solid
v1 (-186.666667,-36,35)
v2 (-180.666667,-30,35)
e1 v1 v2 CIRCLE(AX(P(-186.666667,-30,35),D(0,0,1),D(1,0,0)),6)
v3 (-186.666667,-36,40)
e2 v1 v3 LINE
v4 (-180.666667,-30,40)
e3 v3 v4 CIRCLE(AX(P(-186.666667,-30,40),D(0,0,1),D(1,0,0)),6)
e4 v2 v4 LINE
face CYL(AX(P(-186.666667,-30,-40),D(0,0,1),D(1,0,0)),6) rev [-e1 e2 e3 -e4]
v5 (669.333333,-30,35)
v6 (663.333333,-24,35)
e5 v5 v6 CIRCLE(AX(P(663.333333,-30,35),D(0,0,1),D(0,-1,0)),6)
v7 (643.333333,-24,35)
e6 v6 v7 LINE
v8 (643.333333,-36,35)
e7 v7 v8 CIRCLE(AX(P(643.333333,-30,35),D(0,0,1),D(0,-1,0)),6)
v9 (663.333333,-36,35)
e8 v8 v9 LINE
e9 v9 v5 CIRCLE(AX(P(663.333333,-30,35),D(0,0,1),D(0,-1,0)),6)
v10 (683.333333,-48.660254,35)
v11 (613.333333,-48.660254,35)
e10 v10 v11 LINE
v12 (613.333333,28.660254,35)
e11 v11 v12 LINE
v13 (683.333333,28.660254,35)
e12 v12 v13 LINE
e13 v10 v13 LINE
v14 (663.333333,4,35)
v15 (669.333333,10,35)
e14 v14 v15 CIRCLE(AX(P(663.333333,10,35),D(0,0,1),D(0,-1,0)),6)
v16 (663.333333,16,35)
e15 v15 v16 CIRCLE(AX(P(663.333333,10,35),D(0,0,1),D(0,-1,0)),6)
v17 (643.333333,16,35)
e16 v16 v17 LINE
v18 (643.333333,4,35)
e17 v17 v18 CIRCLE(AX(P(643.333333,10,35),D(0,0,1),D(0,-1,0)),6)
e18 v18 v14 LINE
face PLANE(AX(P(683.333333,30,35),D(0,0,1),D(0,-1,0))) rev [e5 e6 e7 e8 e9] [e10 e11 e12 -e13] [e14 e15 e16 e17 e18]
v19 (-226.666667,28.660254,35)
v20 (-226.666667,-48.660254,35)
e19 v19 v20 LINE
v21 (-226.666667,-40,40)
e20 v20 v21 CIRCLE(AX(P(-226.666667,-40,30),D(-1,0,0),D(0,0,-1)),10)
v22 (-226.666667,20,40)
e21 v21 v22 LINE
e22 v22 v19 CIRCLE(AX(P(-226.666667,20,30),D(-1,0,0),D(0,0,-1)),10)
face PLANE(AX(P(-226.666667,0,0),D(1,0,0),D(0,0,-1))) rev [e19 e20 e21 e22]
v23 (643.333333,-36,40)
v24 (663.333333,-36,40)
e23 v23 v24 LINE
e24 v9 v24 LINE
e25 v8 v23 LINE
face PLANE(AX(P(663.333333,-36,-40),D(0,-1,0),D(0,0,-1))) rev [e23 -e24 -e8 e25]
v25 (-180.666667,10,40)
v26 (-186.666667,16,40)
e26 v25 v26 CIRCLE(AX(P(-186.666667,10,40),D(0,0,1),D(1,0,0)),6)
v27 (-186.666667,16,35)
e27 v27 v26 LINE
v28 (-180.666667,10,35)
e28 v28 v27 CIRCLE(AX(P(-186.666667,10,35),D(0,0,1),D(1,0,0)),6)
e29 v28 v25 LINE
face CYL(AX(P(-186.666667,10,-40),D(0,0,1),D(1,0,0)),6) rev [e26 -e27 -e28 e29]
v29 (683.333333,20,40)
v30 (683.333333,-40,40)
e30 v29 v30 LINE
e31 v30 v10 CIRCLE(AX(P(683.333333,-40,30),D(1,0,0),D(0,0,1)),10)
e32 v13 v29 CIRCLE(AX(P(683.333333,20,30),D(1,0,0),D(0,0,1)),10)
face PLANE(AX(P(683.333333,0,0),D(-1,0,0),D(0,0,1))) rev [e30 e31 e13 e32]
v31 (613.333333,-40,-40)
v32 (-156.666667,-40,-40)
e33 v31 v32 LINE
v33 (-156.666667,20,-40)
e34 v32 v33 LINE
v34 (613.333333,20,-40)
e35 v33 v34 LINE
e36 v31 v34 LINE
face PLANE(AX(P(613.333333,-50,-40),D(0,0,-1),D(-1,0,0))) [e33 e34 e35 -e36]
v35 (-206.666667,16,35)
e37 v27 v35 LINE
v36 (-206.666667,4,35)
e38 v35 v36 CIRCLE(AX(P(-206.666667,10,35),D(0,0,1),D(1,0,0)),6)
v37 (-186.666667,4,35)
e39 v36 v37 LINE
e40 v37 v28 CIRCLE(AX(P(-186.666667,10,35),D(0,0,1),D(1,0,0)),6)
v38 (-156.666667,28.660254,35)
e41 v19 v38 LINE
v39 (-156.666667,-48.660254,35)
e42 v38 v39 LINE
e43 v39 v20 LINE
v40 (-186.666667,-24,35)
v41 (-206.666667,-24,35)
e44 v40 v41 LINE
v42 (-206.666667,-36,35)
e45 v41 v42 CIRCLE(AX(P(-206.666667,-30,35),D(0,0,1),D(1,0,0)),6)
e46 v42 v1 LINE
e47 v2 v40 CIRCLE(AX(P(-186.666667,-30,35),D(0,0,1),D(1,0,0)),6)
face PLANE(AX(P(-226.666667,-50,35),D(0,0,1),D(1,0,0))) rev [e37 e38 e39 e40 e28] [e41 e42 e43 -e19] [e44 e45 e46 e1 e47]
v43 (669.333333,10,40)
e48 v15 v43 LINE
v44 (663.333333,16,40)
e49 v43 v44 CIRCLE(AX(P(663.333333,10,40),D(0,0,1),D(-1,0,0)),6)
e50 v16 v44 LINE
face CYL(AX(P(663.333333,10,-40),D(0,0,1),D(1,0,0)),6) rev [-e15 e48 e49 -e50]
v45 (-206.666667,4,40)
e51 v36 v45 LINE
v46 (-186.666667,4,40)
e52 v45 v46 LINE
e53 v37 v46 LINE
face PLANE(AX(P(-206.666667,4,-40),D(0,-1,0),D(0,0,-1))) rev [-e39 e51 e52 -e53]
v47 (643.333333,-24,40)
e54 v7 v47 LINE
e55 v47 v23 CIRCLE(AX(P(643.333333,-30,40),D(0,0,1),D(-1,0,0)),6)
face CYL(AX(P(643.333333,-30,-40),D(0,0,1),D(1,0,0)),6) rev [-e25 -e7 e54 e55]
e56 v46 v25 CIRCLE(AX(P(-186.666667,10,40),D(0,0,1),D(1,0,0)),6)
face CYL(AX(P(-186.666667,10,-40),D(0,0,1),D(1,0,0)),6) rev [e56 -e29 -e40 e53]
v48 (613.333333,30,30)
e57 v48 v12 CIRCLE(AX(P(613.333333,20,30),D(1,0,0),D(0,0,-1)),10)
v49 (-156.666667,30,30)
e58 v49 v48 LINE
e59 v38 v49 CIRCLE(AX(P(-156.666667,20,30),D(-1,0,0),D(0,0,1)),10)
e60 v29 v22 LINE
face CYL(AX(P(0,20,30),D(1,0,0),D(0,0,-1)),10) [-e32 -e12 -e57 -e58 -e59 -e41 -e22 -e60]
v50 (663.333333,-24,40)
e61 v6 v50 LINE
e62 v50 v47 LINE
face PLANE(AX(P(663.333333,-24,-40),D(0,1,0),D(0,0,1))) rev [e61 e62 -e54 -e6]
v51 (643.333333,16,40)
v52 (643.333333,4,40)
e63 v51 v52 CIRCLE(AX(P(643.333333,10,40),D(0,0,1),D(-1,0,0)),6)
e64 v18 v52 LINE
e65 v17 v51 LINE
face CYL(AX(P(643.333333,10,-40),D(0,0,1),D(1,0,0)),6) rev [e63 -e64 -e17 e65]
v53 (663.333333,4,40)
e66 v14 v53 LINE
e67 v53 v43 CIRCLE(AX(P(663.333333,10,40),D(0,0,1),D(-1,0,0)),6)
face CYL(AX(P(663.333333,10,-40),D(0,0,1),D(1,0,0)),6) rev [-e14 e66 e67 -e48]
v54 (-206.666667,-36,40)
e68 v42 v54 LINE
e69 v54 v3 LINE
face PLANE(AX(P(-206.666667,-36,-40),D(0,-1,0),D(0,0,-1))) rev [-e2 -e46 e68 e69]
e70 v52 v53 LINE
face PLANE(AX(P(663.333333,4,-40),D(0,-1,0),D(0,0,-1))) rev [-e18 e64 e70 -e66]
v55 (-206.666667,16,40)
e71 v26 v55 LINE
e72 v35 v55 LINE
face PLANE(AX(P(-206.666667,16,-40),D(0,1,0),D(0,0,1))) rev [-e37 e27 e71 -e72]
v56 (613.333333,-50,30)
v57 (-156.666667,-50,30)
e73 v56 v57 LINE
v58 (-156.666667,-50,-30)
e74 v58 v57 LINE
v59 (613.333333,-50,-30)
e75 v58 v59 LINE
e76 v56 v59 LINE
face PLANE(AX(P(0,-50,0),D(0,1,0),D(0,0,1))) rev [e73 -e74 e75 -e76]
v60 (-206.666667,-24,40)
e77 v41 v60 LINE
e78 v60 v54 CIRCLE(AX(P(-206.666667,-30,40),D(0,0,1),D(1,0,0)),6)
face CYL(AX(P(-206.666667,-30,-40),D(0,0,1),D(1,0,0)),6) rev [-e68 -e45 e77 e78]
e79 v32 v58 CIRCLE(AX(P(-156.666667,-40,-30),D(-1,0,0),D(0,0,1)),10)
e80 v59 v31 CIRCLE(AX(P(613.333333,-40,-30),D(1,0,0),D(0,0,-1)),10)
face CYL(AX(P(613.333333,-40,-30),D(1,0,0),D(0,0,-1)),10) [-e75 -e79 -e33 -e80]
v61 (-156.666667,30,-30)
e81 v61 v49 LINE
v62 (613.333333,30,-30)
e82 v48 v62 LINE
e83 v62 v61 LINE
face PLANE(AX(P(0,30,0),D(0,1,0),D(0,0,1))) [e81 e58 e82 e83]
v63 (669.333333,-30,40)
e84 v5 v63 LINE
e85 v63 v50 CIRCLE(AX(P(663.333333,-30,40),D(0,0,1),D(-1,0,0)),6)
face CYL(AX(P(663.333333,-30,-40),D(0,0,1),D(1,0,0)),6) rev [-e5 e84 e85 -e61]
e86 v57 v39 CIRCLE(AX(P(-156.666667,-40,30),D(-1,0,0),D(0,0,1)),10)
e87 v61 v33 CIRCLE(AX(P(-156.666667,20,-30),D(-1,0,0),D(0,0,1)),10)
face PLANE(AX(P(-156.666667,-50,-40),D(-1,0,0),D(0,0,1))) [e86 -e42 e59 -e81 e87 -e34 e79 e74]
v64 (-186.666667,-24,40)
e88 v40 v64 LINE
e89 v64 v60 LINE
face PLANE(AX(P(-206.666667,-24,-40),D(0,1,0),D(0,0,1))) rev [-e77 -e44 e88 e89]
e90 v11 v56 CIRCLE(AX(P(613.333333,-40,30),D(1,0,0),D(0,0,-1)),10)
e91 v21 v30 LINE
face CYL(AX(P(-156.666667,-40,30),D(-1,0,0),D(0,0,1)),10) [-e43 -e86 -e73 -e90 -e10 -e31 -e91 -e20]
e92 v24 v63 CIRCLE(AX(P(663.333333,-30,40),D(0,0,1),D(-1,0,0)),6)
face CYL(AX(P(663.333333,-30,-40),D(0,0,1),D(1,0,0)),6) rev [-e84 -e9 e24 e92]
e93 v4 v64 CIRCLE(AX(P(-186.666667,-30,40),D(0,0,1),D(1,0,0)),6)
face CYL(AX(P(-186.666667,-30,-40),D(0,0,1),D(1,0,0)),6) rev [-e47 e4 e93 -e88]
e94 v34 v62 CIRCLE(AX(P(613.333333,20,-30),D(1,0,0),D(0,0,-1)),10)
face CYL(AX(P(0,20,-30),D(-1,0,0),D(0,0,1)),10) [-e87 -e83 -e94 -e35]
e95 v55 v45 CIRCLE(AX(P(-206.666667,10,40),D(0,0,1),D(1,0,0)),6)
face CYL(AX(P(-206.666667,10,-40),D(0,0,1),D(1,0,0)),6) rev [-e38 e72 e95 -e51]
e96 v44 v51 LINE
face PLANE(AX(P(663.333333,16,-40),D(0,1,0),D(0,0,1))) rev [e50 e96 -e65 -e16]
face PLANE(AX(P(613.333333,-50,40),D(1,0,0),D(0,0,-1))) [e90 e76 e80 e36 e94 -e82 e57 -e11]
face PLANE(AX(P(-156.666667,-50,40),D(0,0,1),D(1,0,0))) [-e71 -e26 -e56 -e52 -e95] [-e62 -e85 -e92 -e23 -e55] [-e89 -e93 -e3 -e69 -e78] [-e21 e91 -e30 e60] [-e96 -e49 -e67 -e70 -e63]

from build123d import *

# Parameters (mm, degrees)
SKETCH1_W           = 770
SKETCH1_H           = 80
BOSS_EXTRUDE1_DEPTH = 80
SKETCH3_W           = 5
SKETCH3_H           = 80
BOSS_EXTRUDE2_DEPTH = 70
SKETCH4_W           = 5
SKETCH4_H           = 80
BOSS_EXTRUDE3_DEPTH = 70
FILLET2_R           = 10
CUT_EXTRUDE1_DEPTH  = 690.814789958


with BuildPart() as part:
    # Sketch1 → Boss-Extrude1 (new body)
    with BuildSketch(Plane(origin=(0, 30, 0), x_dir=(1, 0, 0), z_dir=(0, 1, 0))):
        with Locations((228.333333333, 0)):
            Rectangle(SKETCH1_W, SKETCH1_H)
    extrude(amount=-BOSS_EXTRUDE1_DEPTH)

    # Sketch3 → Boss-Extrude2 (add)
    with BuildSketch(Plane.ZY.offset(156.666666667)):
        with Locations((37.5, -10)):
            Rectangle(SKETCH3_W, SKETCH3_H)
    extrude(amount=BOSS_EXTRUDE2_DEPTH)

    # Sketch4 → Boss-Extrude3 (add)
    with BuildSketch(Plane(origin=(613.333333333, 0, 0), x_dir=(0, 0, -1), z_dir=(1, 0, 0))):
        with Locations((-37.5, -10)):
            Rectangle(SKETCH4_W, SKETCH4_H)
    extrude(amount=BOSS_EXTRUDE3_DEPTH)

    # Fillet2
    fillet2_edges = [part.edges().sort_by_distance(p)[0] for p in [
        (228.333333333, 30, 40),
        (228.333333333, -50, 40),
        (228.333333333, -50, -40),
        (228.333333333, 30, -40),
    ]]
    fillet(fillet2_edges, radius=FILLET2_R)

    # Sketch6 → Cut-Extrude1 (cut, through all)
    with BuildSketch(Plane.XY.offset(40)):
        with BuildLine():
            Line((-206.666666667, -24), (-186.666666667, -24))
            ThreePointArc((-186.666666667, -24), (-180.666666667, -30), (-186.666666667, -36))
            Line((-186.666666667, -36), (-206.666666667, -36))
            ThreePointArc((-206.666666667, -36), (-212.666666667, -30), (-206.666666667, -24))
        make_face()
        with BuildLine():
            Line((-206.666666667, 16), (-186.666666667, 16))
            ThreePointArc((-186.666666667, 16), (-180.666666667, 10), (-186.666666667, 4))
            Line((-186.666666667, 4), (-206.666666667, 4))
            ThreePointArc((-206.666666667, 4), (-212.666666667, 10), (-206.666666667, 16))
        make_face()
        with BuildLine():
            Line((663.333333333, 16), (643.333333333, 16))
            ThreePointArc((643.333333333, 16), (637.333333333, 10), (643.333333333, 4))
            Line((643.333333333, 4), (663.333333333, 4))
            ThreePointArc((663.333333333, 4), (669.333333333, 10), (663.333333333, 16))
        make_face()
        with BuildLine():
            Line((663.333333333, -24), (643.333333333, -24))
            ThreePointArc((643.333333333, -24), (637.333333333, -30), (643.333333333, -36))
            Line((643.333333333, -36), (663.333333333, -36))
            ThreePointArc((663.333333333, -36), (669.333333333, -30), (663.333333333, -24))
        make_face()
    extrude(amount=-CUT_EXTRUDE1_DEPTH, mode=Mode.SUBTRACT)


solid = part.part
